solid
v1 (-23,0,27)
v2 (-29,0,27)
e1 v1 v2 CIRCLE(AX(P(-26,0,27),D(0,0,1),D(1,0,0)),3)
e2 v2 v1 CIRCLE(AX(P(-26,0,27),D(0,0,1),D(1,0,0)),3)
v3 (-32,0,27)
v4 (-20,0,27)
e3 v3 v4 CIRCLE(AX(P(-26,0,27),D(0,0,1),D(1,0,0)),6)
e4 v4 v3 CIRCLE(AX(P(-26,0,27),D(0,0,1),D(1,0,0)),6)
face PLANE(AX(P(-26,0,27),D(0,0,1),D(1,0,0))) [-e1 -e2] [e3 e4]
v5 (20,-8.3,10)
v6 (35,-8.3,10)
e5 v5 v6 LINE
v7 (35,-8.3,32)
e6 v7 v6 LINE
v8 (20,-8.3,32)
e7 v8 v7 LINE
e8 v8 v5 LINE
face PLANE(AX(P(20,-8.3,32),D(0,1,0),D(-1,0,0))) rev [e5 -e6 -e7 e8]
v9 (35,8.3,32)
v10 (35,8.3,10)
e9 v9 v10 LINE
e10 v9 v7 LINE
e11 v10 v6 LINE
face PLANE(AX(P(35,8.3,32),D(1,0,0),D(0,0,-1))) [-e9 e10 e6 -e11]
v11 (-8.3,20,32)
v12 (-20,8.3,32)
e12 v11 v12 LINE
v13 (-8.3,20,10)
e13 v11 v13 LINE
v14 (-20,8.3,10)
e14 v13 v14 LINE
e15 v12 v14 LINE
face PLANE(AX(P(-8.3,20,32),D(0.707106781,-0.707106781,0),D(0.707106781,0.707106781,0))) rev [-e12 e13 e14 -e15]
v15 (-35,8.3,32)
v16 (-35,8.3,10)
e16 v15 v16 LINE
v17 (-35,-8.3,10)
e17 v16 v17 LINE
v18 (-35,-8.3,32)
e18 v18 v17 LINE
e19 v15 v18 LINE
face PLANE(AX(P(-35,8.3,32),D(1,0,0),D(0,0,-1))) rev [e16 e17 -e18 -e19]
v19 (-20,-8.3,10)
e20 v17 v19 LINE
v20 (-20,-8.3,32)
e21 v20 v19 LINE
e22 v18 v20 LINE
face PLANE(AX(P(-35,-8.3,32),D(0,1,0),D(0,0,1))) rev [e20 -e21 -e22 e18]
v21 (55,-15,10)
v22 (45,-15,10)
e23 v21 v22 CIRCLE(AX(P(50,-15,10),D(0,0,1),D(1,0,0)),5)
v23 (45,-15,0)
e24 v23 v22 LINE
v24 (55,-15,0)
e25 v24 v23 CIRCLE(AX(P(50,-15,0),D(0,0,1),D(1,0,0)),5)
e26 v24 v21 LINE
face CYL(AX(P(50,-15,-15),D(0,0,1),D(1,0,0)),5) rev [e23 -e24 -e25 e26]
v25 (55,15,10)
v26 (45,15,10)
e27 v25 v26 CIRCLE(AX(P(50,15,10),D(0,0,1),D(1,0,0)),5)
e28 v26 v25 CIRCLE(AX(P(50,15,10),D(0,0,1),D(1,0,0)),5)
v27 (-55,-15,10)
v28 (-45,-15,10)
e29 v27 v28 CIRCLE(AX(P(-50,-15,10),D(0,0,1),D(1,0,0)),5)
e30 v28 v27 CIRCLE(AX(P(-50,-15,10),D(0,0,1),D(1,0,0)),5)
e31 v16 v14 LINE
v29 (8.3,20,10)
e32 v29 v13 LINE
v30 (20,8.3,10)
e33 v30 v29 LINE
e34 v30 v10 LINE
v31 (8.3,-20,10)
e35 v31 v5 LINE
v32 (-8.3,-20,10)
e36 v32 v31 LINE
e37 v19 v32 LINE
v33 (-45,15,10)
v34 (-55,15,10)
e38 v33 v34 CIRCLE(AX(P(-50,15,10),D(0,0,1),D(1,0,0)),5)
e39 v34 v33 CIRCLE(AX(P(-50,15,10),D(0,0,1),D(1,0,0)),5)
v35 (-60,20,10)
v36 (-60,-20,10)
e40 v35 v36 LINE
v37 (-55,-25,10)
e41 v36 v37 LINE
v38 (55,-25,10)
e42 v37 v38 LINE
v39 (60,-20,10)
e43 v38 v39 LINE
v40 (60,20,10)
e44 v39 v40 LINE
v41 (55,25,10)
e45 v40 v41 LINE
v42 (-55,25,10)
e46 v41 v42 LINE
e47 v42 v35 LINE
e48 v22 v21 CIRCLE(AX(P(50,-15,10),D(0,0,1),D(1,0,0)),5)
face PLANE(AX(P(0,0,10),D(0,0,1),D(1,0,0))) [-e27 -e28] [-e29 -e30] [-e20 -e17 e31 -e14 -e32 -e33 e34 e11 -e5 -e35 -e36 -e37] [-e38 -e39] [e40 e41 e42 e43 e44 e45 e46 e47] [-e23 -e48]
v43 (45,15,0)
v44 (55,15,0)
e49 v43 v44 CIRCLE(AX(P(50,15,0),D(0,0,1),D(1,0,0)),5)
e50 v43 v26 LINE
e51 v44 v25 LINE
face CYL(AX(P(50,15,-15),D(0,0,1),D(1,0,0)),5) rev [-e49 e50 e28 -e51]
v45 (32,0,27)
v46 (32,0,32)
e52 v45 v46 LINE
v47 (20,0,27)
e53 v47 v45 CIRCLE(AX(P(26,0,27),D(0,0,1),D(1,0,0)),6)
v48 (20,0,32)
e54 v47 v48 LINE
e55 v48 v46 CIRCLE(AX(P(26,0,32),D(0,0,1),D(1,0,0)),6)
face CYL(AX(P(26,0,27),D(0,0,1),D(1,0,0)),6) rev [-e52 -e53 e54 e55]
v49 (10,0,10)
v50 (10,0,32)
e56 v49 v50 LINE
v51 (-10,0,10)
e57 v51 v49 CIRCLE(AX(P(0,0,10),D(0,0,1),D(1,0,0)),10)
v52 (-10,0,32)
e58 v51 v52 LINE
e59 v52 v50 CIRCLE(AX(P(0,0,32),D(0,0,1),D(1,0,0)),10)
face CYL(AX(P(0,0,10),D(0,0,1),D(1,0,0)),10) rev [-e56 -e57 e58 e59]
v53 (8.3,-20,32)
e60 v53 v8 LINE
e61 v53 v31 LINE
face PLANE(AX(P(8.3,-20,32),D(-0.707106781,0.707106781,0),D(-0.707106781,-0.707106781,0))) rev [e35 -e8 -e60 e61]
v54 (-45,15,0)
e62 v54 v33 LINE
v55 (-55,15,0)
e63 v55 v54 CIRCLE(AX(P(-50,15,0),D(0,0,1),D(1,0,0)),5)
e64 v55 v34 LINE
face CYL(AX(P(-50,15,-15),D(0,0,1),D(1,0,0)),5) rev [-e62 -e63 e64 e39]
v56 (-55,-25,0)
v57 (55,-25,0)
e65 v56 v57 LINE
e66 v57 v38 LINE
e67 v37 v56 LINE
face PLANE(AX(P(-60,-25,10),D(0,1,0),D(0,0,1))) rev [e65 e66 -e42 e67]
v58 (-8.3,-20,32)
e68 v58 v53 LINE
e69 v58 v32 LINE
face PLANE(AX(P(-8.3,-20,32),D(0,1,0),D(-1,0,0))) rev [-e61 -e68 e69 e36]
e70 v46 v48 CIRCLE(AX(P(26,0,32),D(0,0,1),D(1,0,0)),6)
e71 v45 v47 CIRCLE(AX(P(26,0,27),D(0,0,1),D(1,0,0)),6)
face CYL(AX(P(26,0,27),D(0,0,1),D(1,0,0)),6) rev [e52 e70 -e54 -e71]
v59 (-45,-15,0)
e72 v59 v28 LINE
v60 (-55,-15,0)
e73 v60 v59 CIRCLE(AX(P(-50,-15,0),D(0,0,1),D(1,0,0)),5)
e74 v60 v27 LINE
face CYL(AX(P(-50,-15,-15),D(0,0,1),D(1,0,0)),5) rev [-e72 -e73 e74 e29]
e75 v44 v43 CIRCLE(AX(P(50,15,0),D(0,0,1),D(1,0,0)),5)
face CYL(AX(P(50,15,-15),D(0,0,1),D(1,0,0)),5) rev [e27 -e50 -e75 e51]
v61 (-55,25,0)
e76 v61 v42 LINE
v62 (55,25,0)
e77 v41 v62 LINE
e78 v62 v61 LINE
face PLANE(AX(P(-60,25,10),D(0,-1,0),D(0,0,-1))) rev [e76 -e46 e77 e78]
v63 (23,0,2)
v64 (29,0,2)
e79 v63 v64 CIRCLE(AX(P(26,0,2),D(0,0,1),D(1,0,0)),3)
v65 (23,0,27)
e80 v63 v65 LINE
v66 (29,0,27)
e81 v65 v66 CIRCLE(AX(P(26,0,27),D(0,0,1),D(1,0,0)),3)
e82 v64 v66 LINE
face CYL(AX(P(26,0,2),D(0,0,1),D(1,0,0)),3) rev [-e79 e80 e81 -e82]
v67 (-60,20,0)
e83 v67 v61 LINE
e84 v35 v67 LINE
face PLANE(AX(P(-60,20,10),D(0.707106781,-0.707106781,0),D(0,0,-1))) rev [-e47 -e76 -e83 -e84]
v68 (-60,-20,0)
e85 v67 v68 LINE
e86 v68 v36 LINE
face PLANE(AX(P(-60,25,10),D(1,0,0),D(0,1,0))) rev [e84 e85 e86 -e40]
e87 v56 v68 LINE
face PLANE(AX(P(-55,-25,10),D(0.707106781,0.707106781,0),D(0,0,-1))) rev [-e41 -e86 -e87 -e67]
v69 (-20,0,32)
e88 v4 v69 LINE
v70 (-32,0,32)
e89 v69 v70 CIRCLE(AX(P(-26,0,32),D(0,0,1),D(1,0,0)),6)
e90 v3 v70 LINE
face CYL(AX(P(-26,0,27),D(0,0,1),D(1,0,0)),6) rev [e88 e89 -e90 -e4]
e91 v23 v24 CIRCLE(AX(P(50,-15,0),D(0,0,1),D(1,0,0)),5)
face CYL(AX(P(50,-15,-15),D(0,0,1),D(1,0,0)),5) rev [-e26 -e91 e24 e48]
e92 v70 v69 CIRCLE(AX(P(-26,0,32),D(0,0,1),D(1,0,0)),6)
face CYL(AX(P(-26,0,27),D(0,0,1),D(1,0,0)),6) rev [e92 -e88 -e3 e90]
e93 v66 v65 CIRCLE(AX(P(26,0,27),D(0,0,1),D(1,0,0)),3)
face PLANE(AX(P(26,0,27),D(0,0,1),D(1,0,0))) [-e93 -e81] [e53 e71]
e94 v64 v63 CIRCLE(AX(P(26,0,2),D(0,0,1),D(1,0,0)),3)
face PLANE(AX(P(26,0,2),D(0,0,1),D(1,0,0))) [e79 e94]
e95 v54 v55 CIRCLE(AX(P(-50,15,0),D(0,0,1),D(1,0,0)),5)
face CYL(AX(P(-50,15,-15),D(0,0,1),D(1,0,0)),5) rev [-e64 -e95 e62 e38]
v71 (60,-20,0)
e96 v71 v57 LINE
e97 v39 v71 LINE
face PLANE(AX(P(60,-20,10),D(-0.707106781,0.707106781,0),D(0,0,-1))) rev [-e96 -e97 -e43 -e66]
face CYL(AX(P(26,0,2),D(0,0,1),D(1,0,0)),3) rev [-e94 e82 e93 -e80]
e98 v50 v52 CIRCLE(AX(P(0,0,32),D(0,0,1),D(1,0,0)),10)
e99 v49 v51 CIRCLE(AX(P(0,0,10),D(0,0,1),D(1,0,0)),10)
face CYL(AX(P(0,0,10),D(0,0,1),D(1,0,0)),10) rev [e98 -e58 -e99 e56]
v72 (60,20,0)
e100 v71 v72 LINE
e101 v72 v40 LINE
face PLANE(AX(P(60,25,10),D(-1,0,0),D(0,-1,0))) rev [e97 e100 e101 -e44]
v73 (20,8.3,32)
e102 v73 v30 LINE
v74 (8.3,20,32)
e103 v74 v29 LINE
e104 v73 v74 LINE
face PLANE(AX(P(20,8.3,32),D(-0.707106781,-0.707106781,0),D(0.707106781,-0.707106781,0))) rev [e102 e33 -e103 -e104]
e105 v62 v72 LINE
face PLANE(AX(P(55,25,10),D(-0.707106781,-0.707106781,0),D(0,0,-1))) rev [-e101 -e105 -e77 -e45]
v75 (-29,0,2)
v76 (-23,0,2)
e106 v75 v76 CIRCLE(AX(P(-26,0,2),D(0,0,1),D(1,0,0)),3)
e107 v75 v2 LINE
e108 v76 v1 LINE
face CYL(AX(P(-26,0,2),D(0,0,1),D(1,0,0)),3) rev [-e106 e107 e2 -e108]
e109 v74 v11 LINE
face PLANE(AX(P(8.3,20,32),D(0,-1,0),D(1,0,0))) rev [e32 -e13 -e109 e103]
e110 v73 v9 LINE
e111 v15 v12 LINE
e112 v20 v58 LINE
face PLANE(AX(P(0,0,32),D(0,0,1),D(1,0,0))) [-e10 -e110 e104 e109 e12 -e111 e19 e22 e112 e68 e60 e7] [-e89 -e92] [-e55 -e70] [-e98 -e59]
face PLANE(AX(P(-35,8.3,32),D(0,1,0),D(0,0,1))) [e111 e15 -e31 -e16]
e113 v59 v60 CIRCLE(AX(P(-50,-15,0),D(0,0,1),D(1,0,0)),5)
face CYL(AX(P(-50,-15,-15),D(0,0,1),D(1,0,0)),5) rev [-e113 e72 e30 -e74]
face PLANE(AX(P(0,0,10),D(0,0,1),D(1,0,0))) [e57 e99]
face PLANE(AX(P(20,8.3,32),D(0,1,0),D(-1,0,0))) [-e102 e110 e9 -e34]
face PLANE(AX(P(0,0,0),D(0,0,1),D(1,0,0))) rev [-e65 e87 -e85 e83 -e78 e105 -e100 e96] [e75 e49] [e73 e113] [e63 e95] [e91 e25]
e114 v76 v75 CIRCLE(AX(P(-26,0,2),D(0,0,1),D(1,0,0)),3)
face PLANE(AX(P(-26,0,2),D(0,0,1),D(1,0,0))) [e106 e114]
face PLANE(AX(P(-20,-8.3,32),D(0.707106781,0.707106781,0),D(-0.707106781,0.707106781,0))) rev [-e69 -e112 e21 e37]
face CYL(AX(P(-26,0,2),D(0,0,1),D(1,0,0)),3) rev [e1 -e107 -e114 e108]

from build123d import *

# Parameters (mm, degrees)
BASE_PLATE_SKETCH_W        = 120
BASE_PLATE_SKETCH_H        = 50
BASE_PLATE_120X50X10_DEPTH = 10
CLAMP_BOSS_DEPTH           = 22
BORE_SKETCH_R              = 10
BORE_20_DEPTH              = 22
COUNTERBORE_SKETCH_R       = 6
COUNTERBORES_2X_12_DEPTH   = 5
BOLT_HOLE_SKETCH_R         = 3
BOLT_HOLES_2X_6_DEPTH      = 25
MOUNTING_HOLE_SKETCH_R     = 5
MOUNTING_HOLES_4X_10_DEPTH = 25
CORNER_CHAMFERS_5MM_SIZE   = 5


with BuildPart() as part:
    # Base Plate Sketch → Base Plate 120x50x10 (new body)
    with BuildSketch(Plane.XY):
        Rectangle(BASE_PLATE_SKETCH_W, BASE_PLATE_SKETCH_H)
    extrude(amount=BASE_PLATE_120X50X10_DEPTH)

    # Clamp Boss Sketch → Clamp Boss (add)
    with BuildSketch(Plane.XY.offset(10)):
        Polygon((20, 8.3), (35, 8.3), (35, -8.3), (20, -8.3), (8.3, -20), (-8.3, -20), (-20, -8.3), (-35, -8.3), (-35, 8.3), (-20, 8.3), (-8.3, 20), (8.3, 20), align=None)
    extrude(amount=CLAMP_BOSS_DEPTH)

    # Bore Sketch → Bore Ø20 (cut)
    with BuildSketch(Plane.XY.offset(32)):
        Circle(BORE_SKETCH_R)
    extrude(amount=-BORE_20_DEPTH, mode=Mode.SUBTRACT)

    # Counterbore Sketch → Counterbores 2xØ12 (cut)
    with BuildSketch(Plane.XY.offset(32)):
        with Locations((-26, 0)):
            Circle(COUNTERBORE_SKETCH_R)
        with Locations((26, 0)):
            Circle(COUNTERBORE_SKETCH_R)
    extrude(amount=-COUNTERBORES_2X_12_DEPTH, mode=Mode.SUBTRACT)

    # Bolt Hole Sketch → Bolt Holes 2xØ6 (cut)
    with BuildSketch(Plane.XY.offset(27)):
        with Locations((-26, 0)):
            Circle(BOLT_HOLE_SKETCH_R)
        with Locations((26, 0)):
            Circle(BOLT_HOLE_SKETCH_R)
    extrude(amount=-BOLT_HOLES_2X_6_DEPTH, mode=Mode.SUBTRACT)

    # Mounting Hole Sketch → Mounting Holes 4xØ10 (cut)
    with BuildSketch(Plane.XY.offset(10)):
        with Locations((50, 15)):
            Circle(MOUNTING_HOLE_SKETCH_R)
        with Locations((50, -15)):
            Circle(MOUNTING_HOLE_SKETCH_R)
        with Locations((-50, 15)):
            Circle(MOUNTING_HOLE_SKETCH_R)
        with Locations((-50, -15)):
            Circle(MOUNTING_HOLE_SKETCH_R)
    extrude(amount=-MOUNTING_HOLES_4X_10_DEPTH, mode=Mode.SUBTRACT)

    # Corner Chamfers 5mm
    corner_chamfers_5mm_edges = [part.edges().sort_by_distance(p)[0] for p in [
        (60, -25, 5),
        (-60, -25, 5),
        (-60, 25, 5),
        (60, 25, 5),
    ]]
    chamfer(corner_chamfers_5mm_edges, length=CORNER_CHAMFERS_5MM_SIZE)


solid = part.part
